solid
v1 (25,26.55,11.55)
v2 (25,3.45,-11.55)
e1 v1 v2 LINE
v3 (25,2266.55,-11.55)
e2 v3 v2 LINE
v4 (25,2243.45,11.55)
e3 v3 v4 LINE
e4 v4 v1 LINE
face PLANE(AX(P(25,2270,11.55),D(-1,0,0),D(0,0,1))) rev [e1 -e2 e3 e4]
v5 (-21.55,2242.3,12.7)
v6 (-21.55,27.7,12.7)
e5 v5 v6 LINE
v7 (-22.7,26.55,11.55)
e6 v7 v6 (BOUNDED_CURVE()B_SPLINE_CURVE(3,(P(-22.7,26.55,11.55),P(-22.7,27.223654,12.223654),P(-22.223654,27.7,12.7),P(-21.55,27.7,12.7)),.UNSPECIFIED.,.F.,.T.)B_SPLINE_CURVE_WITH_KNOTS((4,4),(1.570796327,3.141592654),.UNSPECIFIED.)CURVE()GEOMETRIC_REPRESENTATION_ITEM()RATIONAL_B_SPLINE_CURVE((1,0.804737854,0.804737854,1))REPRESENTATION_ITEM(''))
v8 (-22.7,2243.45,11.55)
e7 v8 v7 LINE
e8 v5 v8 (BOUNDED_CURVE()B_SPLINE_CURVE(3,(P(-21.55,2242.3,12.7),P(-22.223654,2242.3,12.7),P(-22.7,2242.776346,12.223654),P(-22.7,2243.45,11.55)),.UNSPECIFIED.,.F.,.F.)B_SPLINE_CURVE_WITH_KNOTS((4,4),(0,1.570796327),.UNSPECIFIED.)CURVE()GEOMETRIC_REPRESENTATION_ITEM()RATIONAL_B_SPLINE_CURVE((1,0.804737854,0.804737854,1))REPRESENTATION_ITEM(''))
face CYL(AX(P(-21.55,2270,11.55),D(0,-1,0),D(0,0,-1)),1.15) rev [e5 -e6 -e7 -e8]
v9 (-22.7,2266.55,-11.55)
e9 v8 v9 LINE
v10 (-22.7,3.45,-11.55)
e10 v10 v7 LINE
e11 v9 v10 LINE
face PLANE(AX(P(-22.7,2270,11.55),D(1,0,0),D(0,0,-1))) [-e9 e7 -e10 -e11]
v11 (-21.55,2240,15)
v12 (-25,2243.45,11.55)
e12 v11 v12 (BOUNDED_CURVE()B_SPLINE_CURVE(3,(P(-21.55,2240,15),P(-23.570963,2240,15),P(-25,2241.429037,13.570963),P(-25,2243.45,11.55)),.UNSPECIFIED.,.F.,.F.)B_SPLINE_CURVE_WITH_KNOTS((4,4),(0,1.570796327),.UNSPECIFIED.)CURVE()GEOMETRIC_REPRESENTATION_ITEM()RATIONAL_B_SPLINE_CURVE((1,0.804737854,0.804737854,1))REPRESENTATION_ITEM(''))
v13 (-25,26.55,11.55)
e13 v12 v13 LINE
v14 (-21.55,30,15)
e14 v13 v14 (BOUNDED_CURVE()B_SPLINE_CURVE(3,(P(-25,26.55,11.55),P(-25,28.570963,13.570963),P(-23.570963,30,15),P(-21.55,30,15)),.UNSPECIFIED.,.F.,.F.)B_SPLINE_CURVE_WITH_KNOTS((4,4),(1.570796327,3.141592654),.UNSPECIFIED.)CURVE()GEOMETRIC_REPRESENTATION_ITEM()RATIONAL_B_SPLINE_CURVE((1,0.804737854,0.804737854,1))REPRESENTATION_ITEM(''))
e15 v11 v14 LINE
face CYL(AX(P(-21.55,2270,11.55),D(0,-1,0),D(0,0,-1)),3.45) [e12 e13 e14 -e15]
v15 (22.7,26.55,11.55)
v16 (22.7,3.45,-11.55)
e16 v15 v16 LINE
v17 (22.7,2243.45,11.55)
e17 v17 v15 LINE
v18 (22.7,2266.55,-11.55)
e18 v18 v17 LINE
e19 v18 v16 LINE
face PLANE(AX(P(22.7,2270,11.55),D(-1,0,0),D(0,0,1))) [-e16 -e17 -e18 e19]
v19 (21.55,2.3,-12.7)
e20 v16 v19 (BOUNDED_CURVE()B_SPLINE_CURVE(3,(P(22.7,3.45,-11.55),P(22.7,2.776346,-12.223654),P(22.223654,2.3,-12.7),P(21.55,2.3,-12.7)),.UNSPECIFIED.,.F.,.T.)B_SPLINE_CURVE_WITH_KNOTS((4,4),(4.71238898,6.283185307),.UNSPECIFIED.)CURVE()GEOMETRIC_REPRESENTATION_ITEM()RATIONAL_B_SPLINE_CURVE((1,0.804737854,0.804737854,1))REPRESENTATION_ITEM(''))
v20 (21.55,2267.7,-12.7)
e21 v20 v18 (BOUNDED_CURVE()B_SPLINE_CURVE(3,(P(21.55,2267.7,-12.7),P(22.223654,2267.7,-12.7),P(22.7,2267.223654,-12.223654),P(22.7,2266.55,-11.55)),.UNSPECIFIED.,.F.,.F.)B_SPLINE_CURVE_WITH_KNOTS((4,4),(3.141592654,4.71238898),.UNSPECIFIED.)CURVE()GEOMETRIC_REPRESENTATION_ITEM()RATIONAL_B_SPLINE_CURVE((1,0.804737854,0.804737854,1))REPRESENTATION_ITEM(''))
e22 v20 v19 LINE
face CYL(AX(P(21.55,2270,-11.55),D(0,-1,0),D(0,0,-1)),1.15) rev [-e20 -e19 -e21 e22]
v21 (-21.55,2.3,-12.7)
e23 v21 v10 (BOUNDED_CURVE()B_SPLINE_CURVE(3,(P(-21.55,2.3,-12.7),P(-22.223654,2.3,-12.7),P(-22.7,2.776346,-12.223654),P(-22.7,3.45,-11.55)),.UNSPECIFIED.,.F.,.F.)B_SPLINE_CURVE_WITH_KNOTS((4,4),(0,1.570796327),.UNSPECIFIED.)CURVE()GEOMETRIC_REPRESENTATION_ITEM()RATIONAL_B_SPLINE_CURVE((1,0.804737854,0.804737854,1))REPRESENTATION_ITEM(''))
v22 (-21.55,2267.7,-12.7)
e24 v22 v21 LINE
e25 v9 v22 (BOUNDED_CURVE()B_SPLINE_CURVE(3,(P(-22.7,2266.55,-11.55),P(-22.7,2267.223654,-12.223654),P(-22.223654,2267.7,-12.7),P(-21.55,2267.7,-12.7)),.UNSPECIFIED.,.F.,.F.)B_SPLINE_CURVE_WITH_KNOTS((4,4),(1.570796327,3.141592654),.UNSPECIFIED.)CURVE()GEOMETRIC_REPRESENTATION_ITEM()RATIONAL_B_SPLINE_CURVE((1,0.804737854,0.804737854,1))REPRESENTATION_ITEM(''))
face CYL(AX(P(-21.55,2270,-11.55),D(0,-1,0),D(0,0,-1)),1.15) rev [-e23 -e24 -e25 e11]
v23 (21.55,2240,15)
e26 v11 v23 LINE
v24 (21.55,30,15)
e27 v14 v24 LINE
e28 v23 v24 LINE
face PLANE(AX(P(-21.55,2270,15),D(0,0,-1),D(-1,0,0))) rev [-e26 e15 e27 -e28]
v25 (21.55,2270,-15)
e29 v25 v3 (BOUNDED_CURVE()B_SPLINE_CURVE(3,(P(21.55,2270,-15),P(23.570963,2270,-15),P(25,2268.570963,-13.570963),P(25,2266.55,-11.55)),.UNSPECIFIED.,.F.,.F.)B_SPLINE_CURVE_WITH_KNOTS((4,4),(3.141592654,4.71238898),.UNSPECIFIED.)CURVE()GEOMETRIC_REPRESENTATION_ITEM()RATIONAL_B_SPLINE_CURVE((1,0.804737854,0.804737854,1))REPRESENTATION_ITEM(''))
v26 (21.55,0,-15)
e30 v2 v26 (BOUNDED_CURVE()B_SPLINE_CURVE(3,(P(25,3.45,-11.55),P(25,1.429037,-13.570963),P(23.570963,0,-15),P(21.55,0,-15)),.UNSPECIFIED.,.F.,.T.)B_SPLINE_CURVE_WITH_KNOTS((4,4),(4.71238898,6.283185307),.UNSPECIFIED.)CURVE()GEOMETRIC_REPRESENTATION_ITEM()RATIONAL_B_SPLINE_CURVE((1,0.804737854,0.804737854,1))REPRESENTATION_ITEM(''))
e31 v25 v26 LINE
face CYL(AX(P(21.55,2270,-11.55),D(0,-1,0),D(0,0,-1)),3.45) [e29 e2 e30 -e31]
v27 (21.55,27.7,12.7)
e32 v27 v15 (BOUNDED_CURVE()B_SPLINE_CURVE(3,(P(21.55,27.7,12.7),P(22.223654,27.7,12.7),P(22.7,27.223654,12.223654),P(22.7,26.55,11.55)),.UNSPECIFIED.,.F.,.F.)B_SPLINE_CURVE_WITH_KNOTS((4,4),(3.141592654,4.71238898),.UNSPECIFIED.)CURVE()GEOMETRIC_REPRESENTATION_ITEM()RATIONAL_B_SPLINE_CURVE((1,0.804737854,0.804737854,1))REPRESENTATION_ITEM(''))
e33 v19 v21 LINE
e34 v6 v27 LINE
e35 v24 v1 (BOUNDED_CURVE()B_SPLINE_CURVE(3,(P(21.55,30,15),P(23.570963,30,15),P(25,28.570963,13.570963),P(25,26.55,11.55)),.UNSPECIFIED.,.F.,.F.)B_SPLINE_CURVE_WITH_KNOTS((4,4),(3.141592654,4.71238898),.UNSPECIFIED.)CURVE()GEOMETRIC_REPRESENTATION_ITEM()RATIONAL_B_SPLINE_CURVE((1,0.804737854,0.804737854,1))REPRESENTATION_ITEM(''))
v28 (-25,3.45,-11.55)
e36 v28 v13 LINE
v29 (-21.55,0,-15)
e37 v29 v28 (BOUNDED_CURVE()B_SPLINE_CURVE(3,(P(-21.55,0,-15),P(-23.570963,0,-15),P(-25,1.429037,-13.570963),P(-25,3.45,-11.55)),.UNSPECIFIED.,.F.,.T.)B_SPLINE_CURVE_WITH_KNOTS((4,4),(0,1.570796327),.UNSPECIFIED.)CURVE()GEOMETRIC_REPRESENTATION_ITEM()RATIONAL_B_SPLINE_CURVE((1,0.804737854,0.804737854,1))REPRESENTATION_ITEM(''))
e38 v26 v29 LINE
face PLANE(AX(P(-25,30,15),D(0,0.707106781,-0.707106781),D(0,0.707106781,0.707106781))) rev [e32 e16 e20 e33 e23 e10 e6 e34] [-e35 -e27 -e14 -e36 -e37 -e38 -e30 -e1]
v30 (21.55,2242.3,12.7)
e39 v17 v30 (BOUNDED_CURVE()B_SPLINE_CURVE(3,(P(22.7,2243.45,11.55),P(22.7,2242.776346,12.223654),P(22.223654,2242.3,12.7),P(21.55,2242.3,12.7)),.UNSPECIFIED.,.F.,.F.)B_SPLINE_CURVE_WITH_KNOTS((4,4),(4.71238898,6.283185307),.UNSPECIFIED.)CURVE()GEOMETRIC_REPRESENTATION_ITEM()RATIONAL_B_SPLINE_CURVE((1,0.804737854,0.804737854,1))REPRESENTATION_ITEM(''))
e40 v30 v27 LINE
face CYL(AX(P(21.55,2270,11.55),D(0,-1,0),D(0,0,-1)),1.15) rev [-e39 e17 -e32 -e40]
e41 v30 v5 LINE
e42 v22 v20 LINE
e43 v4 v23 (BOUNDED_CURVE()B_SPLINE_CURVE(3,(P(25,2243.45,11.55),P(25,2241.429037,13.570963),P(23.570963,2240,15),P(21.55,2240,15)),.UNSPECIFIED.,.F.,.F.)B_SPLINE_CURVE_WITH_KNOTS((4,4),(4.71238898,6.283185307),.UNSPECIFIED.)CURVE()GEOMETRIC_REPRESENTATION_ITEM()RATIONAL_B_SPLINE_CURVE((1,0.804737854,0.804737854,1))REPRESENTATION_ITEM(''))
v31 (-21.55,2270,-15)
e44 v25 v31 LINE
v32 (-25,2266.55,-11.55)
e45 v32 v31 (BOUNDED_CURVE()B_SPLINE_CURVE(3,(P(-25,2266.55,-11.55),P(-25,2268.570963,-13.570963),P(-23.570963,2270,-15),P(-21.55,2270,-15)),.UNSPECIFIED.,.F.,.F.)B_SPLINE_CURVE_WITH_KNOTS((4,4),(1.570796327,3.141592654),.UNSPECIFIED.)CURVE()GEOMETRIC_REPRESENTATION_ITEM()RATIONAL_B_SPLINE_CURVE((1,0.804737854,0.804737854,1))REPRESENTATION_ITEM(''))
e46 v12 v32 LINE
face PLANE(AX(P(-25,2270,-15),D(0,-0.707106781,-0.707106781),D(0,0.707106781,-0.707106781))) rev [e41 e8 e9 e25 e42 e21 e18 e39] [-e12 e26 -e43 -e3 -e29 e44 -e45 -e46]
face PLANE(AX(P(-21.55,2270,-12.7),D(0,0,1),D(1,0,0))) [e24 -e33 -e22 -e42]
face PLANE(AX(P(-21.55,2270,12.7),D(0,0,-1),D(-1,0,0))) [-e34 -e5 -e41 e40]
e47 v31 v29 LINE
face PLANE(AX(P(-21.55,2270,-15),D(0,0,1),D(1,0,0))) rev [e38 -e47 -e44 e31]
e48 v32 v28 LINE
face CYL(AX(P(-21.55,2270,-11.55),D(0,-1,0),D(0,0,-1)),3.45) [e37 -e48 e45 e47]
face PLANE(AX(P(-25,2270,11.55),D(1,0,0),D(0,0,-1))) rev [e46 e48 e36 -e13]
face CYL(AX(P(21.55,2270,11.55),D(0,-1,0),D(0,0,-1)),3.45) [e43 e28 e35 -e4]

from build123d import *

# Parameters (mm, degrees)
BOSS_EXTRUDE1_DEPTH     = 2270
CUT_EXTRUDE1_DEPTH      = 2271.600140932
CUT_EXTRUDE1_DEPTH_BACK = 2271.600140932


with BuildPart() as part:
    # Sketch1 → Boss-Extrude1 (new body)
    with BuildSketch(Plane(origin=(0, 0, 0), x_dir=(1, 0, 0), z_dir=(0, 1, 0))):
        with BuildLine():
            Line((-21.55, -15), (21.55, -15))
            ThreePointArc((21.55, -15), (23.989518395, -13.989518395), (25, -11.55))
            Line((25, -11.55), (25, 11.55))
            ThreePointArc((25, 11.55), (23.989518395, 13.989518395), (21.55, 15))
            Line((21.55, 15), (-21.55, 15))
            ThreePointArc((-21.55, 15), (-23.989518395, 13.989518395), (-25, 11.55))
            Line((-25, 11.55), (-25, -11.55))
            ThreePointArc((-25, -11.55), (-23.989518395, -13.989518395), (-21.55, -15))
        make_face()
        with BuildLine():
            Line((-21.55, -12.7), (21.55, -12.7))
            ThreePointArc((21.55, -12.7), (22.363172798, -12.363172798), (22.7, -11.55))
            Line((22.7, -11.55), (22.7, 11.55))
            ThreePointArc((22.7, 11.55), (22.363172798, 12.363172798), (21.55, 12.7))
            Line((21.55, 12.7), (-21.55, 12.7))
            ThreePointArc((-21.55, 12.7), (-22.363172798, 12.363172798), (-22.7, 11.55))
            Line((-22.7, 11.55), (-22.7, -11.55))
            ThreePointArc((-22.7, -11.55), (-22.363172798, -12.363172798), (-21.55, -12.7))
        make_face(mode=Mode.SUBTRACT)
    extrude(amount=BOSS_EXTRUDE1_DEPTH)

    # Sketch2 → Cut-Extrude1 (cut, two sides: drawn at the far end of the back side and taken through both)
    with BuildSketch(Plane(origin=(25, 0, 0), x_dir=(0, 0, -1), z_dir=(1, 0, 0)).offset(-CUT_EXTRUDE1_DEPTH_BACK)):
        Polygon((15, 2270), (-15, 2240), (-15, 2270), align=None)
        Polygon((15, 0), (-15, 0), (-15, 30), align=None)
    extrude(amount=CUT_EXTRUDE1_DEPTH + CUT_EXTRUDE1_DEPTH_BACK, mode=Mode.SUBTRACT)


solid = part.part
